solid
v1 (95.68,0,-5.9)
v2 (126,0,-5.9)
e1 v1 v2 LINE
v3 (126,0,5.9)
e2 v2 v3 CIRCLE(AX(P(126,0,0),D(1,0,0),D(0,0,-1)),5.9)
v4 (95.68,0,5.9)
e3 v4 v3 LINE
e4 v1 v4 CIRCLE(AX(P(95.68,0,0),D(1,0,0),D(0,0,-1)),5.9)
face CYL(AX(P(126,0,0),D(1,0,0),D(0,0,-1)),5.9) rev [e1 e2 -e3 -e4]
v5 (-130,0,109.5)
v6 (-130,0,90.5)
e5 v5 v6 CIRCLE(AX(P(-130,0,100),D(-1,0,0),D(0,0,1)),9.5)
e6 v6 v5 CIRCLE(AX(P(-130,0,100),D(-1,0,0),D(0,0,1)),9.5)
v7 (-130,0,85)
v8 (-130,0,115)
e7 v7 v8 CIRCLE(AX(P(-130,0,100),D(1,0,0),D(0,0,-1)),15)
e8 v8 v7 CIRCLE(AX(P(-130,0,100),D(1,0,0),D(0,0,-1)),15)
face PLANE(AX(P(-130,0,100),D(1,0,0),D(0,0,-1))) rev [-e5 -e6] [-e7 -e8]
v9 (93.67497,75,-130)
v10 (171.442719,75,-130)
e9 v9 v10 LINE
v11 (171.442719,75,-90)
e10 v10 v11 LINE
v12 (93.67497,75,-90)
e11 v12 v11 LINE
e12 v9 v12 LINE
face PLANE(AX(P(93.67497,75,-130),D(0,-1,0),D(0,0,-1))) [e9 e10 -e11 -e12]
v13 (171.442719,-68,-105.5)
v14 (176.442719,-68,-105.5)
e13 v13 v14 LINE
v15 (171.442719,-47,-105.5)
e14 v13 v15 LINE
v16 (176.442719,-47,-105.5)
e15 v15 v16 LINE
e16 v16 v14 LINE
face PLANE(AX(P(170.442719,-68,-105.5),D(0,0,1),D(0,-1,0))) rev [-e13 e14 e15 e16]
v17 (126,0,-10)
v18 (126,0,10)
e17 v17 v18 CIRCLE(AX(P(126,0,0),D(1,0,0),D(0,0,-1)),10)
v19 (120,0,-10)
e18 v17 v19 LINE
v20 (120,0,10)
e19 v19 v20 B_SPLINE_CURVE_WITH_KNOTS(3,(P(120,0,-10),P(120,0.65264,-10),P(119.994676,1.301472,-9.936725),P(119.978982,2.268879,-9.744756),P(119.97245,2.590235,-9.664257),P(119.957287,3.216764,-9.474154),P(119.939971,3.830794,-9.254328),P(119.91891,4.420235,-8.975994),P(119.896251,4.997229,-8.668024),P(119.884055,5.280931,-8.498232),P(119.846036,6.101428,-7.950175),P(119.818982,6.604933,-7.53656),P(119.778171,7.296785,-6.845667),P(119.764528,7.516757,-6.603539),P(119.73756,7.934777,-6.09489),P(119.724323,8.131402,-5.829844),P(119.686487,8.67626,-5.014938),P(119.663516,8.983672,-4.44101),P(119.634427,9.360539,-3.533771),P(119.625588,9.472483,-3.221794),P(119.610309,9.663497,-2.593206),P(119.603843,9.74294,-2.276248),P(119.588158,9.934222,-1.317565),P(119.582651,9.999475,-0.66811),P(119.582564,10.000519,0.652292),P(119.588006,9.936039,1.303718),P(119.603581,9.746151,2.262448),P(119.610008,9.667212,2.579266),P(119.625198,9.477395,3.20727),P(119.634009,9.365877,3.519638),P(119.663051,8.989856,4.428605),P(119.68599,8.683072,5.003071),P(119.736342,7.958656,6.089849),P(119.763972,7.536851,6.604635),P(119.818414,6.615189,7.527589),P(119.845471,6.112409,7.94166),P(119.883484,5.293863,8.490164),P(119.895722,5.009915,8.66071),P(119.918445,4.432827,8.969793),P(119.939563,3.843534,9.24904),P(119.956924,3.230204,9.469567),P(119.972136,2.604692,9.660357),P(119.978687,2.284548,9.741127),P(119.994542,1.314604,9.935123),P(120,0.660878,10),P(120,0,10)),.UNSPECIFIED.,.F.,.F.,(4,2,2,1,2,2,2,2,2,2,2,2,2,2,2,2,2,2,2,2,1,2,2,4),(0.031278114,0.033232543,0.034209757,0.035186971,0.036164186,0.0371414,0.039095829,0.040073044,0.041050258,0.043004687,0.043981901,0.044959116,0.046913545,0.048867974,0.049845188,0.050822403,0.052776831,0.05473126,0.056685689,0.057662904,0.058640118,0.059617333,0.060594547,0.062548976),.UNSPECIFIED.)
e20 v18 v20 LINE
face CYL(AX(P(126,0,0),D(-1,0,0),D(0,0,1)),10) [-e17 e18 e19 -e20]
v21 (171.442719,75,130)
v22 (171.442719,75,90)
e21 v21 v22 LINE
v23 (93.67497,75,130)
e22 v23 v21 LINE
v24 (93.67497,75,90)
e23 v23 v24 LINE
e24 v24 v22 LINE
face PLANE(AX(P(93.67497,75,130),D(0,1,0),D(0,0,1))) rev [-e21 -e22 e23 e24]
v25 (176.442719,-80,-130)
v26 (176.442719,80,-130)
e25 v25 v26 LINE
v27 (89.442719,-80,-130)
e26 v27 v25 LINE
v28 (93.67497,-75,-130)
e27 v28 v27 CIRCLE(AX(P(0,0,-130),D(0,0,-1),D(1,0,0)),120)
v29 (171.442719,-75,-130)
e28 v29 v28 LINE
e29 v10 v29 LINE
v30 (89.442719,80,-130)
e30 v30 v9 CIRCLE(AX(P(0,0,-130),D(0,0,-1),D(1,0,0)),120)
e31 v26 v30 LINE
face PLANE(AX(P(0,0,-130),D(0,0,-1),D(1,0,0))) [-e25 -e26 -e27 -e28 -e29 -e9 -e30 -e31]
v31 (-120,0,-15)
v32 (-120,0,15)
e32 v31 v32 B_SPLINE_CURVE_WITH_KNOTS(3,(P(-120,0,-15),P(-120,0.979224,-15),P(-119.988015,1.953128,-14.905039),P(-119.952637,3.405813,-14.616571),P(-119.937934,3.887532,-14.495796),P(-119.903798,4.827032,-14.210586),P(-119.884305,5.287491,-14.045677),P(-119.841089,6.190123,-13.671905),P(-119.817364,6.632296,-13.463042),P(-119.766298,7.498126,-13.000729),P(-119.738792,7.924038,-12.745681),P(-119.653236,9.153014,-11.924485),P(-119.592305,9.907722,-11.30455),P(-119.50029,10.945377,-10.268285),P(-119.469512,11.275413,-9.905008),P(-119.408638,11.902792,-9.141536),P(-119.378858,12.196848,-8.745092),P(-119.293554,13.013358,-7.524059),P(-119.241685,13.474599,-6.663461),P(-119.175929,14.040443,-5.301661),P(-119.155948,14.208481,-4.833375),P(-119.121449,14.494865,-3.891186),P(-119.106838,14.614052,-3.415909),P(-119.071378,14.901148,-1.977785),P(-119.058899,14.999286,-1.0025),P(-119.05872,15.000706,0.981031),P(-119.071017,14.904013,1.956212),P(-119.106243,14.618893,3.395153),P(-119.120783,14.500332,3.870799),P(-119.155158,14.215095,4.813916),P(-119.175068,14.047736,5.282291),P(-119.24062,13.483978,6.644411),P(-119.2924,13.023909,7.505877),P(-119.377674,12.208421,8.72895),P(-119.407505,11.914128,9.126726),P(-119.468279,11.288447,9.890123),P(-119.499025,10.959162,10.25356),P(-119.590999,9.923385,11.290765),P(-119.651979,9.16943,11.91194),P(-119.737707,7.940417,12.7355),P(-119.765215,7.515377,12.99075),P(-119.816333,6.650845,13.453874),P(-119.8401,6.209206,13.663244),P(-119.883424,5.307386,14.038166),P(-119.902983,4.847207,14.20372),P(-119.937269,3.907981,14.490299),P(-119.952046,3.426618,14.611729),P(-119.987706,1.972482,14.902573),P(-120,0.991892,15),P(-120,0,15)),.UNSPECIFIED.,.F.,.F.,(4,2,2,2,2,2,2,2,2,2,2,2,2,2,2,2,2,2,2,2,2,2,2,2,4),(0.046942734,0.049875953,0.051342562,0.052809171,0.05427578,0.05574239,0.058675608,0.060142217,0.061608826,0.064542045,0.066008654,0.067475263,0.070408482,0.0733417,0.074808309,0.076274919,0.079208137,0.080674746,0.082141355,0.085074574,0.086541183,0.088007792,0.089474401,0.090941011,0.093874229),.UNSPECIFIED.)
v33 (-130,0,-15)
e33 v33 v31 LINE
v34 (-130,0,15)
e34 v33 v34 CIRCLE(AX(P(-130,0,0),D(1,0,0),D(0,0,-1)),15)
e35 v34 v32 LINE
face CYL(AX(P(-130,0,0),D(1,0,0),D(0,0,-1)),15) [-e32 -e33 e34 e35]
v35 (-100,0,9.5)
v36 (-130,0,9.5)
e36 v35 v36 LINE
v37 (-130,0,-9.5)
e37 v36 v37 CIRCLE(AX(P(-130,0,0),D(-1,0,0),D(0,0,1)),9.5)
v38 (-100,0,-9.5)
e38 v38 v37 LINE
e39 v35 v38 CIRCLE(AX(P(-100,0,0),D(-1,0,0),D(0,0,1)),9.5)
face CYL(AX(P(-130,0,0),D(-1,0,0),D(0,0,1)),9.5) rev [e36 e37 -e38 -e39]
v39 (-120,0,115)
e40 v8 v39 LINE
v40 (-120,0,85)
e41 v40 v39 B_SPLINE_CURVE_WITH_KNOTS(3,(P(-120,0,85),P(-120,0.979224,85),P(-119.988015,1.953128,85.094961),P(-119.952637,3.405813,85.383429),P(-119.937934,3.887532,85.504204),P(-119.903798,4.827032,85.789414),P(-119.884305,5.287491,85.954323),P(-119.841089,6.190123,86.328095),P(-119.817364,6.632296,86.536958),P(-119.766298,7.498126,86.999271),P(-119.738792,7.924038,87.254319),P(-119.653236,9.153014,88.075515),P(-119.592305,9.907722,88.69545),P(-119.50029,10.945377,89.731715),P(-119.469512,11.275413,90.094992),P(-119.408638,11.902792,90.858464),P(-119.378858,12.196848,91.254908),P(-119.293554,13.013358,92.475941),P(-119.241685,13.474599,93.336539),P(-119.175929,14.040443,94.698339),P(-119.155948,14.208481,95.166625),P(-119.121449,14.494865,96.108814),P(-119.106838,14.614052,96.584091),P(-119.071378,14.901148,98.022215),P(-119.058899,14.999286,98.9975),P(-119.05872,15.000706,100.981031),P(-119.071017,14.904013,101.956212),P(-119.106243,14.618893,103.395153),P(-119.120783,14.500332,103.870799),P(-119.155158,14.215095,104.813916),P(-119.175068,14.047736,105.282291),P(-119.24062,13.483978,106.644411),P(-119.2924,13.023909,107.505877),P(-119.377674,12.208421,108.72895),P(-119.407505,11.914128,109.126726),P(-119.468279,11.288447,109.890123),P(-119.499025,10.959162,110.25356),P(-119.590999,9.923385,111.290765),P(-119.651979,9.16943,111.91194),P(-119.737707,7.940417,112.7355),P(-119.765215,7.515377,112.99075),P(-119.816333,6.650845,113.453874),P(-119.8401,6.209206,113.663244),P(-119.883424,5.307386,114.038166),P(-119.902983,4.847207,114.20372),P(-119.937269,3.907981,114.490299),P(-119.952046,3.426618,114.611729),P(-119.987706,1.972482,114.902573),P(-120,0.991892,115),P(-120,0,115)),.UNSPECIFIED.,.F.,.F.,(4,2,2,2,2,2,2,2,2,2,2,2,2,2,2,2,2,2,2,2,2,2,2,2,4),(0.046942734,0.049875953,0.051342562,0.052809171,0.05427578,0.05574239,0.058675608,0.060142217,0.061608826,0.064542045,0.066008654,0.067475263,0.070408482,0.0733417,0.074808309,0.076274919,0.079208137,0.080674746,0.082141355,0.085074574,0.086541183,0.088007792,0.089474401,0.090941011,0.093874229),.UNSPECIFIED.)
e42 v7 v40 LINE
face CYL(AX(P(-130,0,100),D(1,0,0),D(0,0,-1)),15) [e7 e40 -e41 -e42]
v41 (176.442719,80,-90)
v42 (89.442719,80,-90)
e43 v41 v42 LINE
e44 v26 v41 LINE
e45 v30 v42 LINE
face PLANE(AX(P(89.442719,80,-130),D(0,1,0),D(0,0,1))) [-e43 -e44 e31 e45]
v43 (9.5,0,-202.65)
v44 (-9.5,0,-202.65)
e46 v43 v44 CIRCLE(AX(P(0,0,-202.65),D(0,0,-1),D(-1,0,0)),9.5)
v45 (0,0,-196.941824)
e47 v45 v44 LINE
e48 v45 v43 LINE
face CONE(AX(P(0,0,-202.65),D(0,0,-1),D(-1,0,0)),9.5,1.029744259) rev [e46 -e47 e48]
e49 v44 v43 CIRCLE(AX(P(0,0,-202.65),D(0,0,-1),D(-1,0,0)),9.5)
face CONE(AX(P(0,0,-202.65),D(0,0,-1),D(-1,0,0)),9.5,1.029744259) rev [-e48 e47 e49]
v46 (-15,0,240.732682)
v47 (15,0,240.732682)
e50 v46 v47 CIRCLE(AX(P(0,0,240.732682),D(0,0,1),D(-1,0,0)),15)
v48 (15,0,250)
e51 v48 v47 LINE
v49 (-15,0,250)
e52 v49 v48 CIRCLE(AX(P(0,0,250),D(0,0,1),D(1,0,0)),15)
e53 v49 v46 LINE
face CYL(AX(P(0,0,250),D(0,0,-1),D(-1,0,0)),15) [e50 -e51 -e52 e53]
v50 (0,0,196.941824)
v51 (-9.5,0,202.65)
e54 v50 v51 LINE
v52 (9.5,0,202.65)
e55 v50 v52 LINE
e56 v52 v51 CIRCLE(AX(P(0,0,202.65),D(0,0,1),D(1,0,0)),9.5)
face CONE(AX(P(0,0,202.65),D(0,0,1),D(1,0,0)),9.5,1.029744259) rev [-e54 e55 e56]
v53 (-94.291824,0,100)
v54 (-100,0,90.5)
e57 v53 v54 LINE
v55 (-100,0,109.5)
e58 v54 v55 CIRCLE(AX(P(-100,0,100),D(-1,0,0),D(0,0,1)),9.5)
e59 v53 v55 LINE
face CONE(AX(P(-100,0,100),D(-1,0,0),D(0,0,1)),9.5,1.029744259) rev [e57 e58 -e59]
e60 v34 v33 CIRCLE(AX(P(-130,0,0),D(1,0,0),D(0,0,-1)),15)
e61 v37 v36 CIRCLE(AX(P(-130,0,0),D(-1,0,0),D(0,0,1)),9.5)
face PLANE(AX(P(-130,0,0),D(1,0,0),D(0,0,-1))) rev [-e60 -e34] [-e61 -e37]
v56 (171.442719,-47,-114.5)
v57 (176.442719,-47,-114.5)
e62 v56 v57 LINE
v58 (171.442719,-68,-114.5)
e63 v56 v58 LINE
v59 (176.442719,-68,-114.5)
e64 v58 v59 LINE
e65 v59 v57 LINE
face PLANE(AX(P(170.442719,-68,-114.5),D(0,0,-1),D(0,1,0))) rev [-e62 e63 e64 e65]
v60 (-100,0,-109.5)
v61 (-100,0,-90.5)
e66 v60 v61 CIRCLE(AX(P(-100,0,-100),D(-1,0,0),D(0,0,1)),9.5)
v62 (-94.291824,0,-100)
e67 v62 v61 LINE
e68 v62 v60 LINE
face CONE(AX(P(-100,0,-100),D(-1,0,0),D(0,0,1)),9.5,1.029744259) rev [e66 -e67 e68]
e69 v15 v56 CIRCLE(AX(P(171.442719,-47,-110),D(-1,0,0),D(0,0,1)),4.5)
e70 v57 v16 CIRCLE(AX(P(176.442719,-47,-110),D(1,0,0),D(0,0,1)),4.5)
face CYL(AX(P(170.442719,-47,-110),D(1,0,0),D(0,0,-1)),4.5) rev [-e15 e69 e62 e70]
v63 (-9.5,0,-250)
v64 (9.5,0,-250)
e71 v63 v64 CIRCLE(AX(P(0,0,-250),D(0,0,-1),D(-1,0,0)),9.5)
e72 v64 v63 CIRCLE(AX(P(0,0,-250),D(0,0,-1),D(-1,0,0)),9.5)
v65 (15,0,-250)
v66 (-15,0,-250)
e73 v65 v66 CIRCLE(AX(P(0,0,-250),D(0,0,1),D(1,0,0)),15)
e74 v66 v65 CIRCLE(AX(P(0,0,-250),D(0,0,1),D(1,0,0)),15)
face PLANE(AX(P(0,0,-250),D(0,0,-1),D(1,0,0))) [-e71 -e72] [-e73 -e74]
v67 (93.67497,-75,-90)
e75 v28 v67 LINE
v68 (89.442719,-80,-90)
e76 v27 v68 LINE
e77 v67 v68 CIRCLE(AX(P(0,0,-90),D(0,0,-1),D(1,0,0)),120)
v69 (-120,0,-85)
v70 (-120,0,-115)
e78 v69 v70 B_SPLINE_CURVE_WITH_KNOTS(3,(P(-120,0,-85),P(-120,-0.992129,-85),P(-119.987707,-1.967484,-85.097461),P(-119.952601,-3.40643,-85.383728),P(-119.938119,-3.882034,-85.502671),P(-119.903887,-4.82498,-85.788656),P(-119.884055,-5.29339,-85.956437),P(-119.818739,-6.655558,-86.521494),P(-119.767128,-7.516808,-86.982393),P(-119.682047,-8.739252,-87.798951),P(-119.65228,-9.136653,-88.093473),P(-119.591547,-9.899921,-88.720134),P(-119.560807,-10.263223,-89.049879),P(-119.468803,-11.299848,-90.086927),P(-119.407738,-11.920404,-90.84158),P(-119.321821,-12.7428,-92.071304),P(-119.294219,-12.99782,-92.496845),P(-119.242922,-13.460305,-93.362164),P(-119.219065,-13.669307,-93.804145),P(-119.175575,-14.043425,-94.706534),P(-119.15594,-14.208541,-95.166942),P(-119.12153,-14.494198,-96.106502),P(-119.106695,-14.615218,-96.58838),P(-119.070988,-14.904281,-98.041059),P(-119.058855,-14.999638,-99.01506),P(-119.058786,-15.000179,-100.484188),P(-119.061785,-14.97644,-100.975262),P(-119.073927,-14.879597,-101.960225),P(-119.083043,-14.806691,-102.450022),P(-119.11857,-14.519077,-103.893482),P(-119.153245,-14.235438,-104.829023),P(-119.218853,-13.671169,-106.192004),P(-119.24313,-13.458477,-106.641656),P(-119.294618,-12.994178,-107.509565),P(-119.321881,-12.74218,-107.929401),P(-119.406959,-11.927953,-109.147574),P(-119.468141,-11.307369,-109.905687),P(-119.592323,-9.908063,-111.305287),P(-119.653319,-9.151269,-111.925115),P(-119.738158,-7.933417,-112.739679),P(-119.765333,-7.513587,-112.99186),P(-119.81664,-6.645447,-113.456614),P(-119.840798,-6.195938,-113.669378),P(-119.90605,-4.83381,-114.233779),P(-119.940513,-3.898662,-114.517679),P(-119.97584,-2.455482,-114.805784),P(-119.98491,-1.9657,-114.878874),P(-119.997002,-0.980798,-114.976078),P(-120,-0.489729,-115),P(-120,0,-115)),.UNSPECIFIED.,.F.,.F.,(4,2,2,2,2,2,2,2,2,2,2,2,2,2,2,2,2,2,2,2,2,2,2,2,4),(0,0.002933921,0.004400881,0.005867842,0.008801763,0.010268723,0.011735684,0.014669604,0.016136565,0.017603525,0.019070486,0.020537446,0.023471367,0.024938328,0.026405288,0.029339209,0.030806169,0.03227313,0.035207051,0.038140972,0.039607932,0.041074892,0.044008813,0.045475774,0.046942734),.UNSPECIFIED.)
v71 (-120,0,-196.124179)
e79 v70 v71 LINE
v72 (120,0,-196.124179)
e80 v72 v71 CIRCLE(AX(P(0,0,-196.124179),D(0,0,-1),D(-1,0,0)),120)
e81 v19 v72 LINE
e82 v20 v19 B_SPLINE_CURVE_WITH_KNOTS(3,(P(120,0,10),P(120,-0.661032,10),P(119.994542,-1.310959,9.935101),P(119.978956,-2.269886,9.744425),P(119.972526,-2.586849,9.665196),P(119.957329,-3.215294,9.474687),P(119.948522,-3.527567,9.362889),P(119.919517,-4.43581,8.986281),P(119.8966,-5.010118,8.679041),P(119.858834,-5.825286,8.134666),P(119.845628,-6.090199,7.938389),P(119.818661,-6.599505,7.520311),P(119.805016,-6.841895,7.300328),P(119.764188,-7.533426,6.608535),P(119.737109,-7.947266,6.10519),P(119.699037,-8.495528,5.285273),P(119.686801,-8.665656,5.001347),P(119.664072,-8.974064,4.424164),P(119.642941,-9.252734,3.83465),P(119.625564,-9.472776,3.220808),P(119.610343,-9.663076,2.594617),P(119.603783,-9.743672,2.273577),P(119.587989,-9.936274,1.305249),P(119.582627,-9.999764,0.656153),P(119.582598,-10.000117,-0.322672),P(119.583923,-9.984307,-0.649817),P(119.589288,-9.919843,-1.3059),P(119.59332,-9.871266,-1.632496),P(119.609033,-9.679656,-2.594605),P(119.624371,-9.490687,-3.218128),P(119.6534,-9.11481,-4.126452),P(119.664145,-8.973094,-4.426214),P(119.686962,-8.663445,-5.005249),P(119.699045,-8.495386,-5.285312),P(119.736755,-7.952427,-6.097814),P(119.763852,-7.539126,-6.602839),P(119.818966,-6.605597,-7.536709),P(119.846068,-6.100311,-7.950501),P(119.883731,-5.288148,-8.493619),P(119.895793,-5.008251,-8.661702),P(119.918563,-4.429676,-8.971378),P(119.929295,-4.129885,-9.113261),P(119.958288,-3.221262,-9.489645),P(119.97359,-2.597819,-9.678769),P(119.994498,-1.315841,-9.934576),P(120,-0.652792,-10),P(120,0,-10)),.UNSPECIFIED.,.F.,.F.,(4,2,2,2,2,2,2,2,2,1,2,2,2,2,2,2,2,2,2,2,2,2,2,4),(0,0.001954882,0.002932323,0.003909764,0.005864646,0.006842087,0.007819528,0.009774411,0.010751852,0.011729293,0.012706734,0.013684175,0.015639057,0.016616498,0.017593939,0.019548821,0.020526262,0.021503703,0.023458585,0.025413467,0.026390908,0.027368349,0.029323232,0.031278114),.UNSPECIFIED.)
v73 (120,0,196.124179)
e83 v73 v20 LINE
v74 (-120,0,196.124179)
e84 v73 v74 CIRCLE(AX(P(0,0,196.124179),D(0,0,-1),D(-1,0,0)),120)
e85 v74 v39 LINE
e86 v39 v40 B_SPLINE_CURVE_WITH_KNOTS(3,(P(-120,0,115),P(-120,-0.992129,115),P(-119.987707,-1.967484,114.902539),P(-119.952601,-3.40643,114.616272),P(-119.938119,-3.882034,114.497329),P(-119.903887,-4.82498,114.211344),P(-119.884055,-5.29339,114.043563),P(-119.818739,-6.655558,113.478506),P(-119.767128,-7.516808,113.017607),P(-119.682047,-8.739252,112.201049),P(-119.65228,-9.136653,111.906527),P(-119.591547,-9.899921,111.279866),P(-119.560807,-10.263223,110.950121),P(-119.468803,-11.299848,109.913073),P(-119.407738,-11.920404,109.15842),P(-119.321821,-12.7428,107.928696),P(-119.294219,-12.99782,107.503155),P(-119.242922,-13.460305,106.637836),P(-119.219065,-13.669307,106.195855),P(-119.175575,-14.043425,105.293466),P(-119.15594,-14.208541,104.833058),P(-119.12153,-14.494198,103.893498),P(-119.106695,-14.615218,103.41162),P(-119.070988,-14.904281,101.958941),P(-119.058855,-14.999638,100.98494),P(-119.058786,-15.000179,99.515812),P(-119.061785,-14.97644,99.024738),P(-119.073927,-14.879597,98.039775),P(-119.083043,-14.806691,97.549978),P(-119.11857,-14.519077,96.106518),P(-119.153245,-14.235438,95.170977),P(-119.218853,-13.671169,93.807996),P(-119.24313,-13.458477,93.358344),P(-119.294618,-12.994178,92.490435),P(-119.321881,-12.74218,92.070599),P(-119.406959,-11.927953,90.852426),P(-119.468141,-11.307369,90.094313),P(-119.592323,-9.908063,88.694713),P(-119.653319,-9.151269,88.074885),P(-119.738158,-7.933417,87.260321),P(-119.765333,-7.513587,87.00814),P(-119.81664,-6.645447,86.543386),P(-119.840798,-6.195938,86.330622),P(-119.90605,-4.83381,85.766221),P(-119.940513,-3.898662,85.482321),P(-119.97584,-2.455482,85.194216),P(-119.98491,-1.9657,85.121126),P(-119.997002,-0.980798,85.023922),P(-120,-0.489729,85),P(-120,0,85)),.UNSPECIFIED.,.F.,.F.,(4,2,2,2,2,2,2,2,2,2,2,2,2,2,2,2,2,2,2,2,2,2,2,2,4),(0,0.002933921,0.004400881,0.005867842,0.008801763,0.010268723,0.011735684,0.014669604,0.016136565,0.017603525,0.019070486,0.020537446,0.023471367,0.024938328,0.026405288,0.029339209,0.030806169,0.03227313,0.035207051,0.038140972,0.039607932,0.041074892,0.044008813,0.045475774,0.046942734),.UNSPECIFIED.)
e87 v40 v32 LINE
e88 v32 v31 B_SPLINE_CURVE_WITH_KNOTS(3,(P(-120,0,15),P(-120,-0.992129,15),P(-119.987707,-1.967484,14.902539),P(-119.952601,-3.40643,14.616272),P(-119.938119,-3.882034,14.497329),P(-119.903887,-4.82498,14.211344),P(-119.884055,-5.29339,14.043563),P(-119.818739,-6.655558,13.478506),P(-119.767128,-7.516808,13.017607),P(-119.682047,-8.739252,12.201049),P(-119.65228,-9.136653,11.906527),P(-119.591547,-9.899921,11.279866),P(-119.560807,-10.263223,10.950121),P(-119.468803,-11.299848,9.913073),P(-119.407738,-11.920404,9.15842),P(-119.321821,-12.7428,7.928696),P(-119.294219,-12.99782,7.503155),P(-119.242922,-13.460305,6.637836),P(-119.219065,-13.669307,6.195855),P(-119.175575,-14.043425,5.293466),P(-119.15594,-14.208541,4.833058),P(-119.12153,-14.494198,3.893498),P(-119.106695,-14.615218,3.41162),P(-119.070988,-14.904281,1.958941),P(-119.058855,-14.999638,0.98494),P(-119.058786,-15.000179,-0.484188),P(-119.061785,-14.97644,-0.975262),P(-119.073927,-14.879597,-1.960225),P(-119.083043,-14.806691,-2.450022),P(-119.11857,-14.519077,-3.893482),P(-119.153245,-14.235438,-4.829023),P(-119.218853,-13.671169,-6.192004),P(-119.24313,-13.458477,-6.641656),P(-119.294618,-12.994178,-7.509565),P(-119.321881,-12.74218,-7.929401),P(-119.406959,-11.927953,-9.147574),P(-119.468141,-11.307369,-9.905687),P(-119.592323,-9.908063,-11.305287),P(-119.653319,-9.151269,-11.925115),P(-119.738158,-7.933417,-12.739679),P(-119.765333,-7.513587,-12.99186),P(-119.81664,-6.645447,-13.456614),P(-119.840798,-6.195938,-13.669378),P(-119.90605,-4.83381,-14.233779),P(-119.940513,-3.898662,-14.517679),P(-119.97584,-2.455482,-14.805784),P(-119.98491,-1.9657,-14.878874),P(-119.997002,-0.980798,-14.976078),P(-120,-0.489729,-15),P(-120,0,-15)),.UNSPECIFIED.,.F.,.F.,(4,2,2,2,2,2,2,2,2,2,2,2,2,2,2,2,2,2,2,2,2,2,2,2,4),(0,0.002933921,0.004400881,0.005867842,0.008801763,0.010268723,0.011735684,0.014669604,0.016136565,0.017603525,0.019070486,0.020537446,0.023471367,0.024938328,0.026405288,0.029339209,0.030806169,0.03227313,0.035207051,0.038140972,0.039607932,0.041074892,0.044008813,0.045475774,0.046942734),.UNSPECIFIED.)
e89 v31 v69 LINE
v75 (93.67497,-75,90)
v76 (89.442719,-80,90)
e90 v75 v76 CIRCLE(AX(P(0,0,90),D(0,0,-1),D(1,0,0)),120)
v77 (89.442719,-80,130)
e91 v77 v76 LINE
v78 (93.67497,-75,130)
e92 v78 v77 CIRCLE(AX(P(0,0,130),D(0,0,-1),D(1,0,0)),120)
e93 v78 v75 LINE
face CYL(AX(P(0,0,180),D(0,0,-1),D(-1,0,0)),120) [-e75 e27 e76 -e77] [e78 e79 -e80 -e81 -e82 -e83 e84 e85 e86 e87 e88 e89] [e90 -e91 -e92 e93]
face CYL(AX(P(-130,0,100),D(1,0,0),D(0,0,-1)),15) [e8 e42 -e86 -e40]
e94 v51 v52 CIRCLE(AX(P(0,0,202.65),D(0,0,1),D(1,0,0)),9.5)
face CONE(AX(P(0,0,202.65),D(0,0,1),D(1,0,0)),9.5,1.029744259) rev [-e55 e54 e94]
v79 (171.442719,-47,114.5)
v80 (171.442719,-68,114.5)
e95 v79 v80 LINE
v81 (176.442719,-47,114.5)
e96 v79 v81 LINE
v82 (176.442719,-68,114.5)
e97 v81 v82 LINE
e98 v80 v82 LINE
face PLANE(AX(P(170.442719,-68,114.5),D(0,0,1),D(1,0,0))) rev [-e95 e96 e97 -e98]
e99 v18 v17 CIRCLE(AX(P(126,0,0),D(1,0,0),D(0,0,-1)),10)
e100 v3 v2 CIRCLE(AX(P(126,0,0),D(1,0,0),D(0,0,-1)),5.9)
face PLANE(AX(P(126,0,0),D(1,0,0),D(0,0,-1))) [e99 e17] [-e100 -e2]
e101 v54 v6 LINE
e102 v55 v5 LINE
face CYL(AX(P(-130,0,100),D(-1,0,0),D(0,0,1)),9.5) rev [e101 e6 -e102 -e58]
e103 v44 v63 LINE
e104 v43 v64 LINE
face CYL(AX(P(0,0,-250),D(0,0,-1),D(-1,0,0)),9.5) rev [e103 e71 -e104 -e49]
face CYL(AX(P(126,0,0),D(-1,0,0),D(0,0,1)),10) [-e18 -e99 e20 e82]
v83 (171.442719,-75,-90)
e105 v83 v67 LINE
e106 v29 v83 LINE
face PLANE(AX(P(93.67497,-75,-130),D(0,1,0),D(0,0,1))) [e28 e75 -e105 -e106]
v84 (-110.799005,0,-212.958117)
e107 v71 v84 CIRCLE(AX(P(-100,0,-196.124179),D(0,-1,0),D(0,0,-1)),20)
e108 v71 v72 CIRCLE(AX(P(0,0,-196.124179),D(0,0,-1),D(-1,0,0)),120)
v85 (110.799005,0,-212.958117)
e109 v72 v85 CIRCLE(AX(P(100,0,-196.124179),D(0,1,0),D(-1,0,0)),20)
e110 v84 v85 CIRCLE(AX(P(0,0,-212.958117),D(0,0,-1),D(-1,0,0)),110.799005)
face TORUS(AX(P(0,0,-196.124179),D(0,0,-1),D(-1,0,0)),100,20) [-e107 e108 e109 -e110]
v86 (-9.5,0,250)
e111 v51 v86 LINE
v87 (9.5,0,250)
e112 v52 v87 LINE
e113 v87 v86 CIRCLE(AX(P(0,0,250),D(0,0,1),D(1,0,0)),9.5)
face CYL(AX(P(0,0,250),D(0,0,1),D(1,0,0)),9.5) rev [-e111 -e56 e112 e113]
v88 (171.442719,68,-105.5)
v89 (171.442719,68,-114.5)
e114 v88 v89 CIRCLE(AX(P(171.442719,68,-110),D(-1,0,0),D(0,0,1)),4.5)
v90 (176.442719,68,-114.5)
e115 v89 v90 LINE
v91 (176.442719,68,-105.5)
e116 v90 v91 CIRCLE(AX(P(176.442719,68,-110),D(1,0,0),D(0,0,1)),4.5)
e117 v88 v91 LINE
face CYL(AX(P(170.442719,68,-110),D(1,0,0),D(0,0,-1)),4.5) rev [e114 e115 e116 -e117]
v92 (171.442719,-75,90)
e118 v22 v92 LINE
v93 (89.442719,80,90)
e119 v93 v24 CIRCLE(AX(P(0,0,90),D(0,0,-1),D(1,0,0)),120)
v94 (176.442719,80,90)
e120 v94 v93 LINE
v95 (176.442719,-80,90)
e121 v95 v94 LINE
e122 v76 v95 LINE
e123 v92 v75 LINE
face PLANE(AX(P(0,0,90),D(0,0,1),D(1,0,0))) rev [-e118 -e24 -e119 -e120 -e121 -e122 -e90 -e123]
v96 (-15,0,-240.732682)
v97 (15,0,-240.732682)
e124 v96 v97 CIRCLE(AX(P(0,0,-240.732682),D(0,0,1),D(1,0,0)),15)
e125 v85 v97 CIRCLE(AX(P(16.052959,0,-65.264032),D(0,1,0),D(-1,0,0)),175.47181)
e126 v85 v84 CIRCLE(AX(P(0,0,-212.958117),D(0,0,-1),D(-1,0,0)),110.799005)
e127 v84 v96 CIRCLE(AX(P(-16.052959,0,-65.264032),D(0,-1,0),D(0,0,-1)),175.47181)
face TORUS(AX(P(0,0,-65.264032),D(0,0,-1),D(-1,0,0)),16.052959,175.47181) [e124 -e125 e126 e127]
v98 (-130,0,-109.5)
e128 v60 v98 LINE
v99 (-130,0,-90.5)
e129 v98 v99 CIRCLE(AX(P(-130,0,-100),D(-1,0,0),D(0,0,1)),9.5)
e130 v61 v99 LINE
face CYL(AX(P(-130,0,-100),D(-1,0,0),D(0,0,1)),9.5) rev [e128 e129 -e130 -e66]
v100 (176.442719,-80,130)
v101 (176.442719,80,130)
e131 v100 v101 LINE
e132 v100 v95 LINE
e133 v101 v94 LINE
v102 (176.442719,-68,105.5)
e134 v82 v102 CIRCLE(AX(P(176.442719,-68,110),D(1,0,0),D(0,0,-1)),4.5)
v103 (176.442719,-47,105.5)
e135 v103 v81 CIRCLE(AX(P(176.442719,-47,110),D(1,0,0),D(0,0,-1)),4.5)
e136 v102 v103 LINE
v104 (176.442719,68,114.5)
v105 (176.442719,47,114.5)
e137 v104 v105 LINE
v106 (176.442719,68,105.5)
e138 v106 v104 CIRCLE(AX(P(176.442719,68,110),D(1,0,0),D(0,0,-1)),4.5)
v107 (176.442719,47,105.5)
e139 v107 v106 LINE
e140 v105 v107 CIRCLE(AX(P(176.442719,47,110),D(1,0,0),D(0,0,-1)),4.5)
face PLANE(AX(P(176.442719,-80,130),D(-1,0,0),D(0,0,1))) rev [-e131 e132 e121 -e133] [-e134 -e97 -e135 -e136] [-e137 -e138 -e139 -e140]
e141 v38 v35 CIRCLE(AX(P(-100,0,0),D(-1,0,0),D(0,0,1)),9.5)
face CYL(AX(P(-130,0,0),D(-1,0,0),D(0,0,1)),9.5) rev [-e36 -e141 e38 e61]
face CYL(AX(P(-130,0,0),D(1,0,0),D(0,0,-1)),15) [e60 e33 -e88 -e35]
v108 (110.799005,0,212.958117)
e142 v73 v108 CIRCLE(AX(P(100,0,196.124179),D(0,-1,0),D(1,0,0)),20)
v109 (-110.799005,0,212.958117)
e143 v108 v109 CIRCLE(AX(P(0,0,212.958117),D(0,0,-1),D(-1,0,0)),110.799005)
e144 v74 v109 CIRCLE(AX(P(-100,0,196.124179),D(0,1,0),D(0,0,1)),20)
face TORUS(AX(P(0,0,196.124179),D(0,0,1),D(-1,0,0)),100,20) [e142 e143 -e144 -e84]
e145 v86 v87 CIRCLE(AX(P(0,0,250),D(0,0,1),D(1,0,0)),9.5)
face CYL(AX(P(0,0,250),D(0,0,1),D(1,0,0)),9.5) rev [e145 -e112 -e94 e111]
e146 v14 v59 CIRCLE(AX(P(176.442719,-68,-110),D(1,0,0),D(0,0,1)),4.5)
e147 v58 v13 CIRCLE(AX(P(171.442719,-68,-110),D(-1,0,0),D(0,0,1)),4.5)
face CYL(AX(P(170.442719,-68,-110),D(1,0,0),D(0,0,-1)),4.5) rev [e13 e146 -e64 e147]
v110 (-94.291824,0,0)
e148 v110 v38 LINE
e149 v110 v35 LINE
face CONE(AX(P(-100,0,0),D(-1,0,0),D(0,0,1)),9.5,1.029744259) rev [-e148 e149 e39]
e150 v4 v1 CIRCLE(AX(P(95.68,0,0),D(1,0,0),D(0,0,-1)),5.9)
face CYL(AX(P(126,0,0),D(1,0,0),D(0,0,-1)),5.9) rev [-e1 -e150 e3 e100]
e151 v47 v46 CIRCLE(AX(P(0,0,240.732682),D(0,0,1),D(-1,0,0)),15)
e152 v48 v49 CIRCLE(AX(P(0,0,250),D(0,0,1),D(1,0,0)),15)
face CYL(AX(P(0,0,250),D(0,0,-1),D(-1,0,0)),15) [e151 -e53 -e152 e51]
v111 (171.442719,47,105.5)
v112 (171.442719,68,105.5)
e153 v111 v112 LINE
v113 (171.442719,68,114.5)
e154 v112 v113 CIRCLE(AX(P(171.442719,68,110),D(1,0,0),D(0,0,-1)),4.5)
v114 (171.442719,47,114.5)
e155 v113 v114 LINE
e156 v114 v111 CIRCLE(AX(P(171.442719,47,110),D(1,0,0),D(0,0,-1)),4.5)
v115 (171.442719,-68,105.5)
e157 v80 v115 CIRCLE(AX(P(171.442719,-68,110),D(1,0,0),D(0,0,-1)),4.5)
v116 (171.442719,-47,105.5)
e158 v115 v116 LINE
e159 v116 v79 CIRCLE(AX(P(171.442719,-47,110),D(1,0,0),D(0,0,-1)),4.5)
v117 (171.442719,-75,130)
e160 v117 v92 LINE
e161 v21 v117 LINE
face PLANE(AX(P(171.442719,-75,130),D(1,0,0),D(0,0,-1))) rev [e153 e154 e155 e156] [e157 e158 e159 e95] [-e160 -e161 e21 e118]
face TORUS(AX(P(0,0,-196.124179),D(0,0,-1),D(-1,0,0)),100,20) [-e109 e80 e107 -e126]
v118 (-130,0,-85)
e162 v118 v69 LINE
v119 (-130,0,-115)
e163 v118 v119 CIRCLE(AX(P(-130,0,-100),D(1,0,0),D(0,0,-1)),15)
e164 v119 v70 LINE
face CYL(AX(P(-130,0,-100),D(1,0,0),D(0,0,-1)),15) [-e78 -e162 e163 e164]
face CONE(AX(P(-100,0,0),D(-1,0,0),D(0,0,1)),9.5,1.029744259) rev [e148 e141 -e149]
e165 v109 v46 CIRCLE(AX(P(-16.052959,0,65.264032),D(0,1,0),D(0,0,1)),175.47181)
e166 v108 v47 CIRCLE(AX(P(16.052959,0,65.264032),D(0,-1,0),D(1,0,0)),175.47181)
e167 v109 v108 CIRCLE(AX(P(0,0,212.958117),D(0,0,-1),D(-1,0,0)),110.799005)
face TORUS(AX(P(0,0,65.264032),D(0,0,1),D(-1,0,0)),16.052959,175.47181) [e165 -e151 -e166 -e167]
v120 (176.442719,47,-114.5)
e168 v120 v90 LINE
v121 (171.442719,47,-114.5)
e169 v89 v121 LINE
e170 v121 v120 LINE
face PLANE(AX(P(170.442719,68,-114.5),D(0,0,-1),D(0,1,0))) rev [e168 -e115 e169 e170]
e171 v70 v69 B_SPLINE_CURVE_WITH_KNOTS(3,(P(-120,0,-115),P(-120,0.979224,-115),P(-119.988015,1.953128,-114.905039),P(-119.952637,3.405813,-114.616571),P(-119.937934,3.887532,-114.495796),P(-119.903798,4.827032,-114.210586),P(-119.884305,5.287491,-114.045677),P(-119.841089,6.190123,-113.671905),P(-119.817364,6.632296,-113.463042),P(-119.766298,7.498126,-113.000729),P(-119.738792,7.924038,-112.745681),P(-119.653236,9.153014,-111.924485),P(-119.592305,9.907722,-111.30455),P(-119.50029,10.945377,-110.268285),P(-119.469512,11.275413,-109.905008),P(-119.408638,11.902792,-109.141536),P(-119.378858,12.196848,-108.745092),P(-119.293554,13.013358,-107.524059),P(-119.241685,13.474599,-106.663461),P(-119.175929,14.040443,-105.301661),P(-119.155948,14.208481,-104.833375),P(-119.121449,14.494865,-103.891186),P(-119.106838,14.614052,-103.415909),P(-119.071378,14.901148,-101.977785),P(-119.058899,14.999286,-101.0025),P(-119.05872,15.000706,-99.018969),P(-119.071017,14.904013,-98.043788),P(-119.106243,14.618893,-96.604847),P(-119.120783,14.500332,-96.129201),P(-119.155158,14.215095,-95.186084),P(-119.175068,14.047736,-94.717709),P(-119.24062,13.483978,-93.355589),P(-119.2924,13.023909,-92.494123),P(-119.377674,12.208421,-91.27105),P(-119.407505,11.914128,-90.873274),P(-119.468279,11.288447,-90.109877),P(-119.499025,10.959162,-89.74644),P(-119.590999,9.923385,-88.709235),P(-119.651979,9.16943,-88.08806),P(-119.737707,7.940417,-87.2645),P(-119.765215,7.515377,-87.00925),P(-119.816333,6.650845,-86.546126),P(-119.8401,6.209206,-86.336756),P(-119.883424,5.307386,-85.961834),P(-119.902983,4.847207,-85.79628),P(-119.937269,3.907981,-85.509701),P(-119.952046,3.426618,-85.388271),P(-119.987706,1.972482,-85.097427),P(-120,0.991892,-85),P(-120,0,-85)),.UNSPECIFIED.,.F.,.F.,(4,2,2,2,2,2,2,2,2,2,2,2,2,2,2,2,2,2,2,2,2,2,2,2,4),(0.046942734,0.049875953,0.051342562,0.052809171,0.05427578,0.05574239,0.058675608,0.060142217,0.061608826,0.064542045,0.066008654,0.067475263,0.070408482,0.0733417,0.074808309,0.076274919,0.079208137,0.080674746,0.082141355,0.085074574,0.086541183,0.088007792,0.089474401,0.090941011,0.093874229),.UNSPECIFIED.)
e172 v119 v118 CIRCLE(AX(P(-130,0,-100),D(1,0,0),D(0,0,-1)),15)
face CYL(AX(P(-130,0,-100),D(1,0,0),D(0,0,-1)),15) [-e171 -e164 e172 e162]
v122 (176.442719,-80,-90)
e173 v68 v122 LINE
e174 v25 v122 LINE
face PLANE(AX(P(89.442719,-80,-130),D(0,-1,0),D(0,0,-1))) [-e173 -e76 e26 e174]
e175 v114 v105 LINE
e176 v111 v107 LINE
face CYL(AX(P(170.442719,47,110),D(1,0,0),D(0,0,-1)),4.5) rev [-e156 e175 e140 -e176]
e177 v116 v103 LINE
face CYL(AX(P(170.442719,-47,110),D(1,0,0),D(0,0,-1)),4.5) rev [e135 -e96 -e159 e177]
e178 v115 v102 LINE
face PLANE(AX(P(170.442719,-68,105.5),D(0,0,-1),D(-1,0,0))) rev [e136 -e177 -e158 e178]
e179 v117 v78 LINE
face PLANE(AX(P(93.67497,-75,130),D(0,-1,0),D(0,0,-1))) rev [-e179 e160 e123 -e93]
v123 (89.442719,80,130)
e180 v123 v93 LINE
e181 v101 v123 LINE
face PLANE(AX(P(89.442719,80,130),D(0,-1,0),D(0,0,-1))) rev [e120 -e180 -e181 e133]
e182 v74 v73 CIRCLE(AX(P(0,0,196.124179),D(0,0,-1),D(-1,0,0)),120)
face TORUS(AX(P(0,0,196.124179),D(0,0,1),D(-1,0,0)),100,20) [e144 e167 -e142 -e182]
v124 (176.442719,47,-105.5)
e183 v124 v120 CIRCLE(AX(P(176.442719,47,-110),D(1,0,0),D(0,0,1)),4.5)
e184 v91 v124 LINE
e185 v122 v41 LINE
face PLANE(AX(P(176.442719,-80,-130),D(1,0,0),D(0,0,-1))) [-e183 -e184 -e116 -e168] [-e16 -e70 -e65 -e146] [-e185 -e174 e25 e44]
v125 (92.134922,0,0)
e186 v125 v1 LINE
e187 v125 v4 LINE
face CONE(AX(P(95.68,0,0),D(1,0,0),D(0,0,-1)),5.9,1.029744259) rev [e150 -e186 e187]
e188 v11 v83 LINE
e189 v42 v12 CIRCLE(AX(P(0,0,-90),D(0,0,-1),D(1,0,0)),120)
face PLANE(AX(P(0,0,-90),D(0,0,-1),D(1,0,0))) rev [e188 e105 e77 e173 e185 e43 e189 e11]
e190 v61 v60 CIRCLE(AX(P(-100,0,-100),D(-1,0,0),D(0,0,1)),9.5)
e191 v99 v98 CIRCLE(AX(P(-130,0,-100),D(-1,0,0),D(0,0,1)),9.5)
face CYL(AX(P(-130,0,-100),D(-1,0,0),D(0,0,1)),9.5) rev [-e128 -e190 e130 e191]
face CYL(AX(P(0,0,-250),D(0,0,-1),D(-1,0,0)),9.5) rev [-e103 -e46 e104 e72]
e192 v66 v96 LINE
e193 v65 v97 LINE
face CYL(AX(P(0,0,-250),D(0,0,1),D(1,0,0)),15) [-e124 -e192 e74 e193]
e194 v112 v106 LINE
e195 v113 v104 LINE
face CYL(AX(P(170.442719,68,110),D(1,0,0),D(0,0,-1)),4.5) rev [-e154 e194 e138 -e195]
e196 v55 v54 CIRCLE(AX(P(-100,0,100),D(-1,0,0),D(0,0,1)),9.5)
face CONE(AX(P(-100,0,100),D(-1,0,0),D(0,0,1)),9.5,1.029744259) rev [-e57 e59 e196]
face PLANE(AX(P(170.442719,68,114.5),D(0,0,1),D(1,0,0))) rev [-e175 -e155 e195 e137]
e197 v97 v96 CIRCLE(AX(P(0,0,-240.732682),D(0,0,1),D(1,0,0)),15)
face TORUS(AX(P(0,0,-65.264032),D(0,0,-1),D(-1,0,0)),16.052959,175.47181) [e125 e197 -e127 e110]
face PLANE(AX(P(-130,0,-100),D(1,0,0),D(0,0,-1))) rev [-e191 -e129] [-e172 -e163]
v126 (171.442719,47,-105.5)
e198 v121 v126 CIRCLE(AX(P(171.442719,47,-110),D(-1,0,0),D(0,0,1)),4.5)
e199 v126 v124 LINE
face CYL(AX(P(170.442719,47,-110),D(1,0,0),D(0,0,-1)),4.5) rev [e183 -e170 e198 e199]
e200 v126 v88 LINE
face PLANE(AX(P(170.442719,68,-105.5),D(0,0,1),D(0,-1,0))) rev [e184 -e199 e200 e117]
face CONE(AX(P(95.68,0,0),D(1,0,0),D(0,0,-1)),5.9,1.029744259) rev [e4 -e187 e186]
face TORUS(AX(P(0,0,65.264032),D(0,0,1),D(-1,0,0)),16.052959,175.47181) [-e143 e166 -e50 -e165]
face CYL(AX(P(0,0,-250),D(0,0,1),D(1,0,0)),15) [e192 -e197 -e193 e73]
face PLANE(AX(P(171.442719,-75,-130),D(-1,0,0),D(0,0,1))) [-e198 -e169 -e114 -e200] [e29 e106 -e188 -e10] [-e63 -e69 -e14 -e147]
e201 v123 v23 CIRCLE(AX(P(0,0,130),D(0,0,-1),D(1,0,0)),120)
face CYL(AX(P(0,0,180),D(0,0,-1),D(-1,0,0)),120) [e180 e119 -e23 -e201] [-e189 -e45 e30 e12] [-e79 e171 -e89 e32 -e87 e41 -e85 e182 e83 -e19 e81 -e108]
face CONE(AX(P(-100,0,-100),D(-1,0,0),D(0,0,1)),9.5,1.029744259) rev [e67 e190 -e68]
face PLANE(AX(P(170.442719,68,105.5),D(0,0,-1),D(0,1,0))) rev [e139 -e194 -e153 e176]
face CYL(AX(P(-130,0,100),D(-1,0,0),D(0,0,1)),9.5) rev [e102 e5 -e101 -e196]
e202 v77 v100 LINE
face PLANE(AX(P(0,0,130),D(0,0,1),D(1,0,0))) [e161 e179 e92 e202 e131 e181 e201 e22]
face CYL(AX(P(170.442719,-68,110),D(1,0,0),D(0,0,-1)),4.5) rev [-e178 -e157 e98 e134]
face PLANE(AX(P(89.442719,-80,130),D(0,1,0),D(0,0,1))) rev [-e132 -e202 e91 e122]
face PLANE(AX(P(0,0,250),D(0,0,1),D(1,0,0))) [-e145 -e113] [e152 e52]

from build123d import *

# Parameters (mm, degrees)
SKETCH_1_R               = 120
EXTRUDE_1_DEPTH          = 180
EXTRUDE_2_DEPTH          = 20
CUT_EXTRUDE_1_DEPTH      = 6
SKETCH_17_R              = 15
EXTRUDE_3_DEPTH          = 20
HOLE_WIZARD_G1_2_1_D     = 19
HOLE_WIZARD_G1_2_1_DEPTH = 30
HOLE_WIZARD_G1_2_1_TIP   = 5.708175881
SKETCH_20_R              = 15
EXTRUDE_4_DEPTH          = 15
HOLE_WIZARD_G1_2_2_D     = 19
HOLE_WIZARD_G1_2_2_DEPTH = 47.35
HOLE_WIZARD_G1_2_2_TIP   = 5.708175881
HOLE_WIZARD_G1_2_3_D     = 19
HOLE_WIZARD_G1_2_3_DEPTH = 47.35
HOLE_WIZARD_G1_2_3_TIP   = 5.708175881
SKETCH_26_R              = 10
EXTRUDE_5_DEPTH          = 16
HOLE_WIZARD_G1_4_1_D     = 11.8
HOLE_WIZARD_G1_4_1_DEPTH = 30.32
HOLE_WIZARD_G1_4_1_TIP   = 3.545077652


with BuildPart() as part:
    # 草图1 → 凸台-拉伸1 (new, symmetric)
    with BuildSketch(Plane.XY):
        with Locations(Location((0, 0, 0), (0, 0, 180))):
            Circle(SKETCH_1_R)
    extrude(amount=EXTRUDE_1_DEPTH, both=True)

    # 草图2 → 旋转1 (revolve)
    with BuildSketch(Plane(origin=(0, 0, 0), x_dir=(1, 0, 0), z_dir=(0, 1, 0)), mode=Mode.PRIVATE) as revolve_1_sk:
        with BuildLine():
            Line((0, 180), (120, 180))
            Line((120, 180), (120, 196.124178579))
            ThreePointArc((120, 196.124178579), (117.549645232, 205.716360408), (110.799004776, 212.958117388))
            ThreePointArc((110.799004776, 212.958117388), (57.657842502, 235.732180627), (0, 240))
            Line((0, 240), (0, 180))
        make_face()
    revolve_1 = revolve(revolve_1_sk.sketch.rotate(Axis((0, 0, -180), (0, 0, 1)), 180), axis=Axis((0, 0, -180), (0, 0, 1)))

    # 镜向1: 旋转1 across plane
    add(revolve_1.mirror(Plane.XY))

    # 草图15 → 凸台-拉伸2 (add, symmetric)
    with BuildSketch(Plane.XY.offset(110)):
        with BuildLine():
            Line((93.674969976, -75), (171.4427191, -75))
            Line((171.4427191, -75), (171.4427191, 75))
            Line((171.4427191, 75), (93.674969976, 75))
            ThreePointArc((93.674969976, 75), (91.592969234, 77.528884855), (89.4427191, 80))
            Line((89.4427191, 80), (176.4427191, 80))
            Line((176.4427191, 80), (176.4427191, -80))
            Line((176.4427191, -80), (89.4427191, -80))
            ThreePointArc((89.4427191, -80), (91.592969234, -77.528884855), (93.674969976, -75))
        make_face()
    extrude_2 = extrude(amount=EXTRUDE_2_DEPTH, both=True)

    # 镜向2: 凸台-拉伸2 across plane
    add(extrude_2.mirror(Plane.XY))

    # 草图16 → 切除-拉伸1 (cut)
    with BuildSketch(Plane(origin=(176.4427191, 0, 0), x_dir=(0, 0, -1), z_dir=(1, 0, 0))):
        with BuildLine():
            Line((-105.5, 68), (-105.5, 47))
            ThreePointArc((-105.5, 47), (-110, 42.5), (-114.5, 47))
            Line((-114.5, 47), (-114.5, 68))
            ThreePointArc((-114.5, 68), (-110, 72.5), (-105.5, 68))
        make_face()
        with BuildLine():
            Line((-114.5, -68), (-114.5, -47))
            ThreePointArc((-114.5, -47), (-110, -42.5), (-105.5, -47))
            Line((-105.5, -47), (-105.5, -68))
            ThreePointArc((-105.5, -68), (-110, -72.5), (-114.5, -68))
        make_face()
        with BuildLine():
            Line((105.5, 68), (105.5, 47))
            ThreePointArc((105.5, 47), (110, 42.5), (114.5, 47))
            Line((114.5, 47), (114.5, 68))
            ThreePointArc((114.5, 68), (110, 72.5), (105.5, 68))
        make_face()
        with BuildLine():
            Line((114.5, -68), (114.5, -47))
            ThreePointArc((114.5, -47), (110, -42.5), (105.5, -47))
            Line((105.5, -47), (105.5, -68))
            ThreePointArc((105.5, -68), (110, -72.5), (114.5, -68))
        make_face()
    extrude(amount=-CUT_EXTRUDE_1_DEPTH, mode=Mode.SUBTRACT)

    # 草图17 → 凸台-拉伸3 (add)
    with BuildSketch(Plane(origin=(-110, 0, 0), x_dir=(0, 0, -1), z_dir=(1, 0, 0))):
        Circle(SKETCH_17_R)
        with Locations((100, 0)):
            Circle(SKETCH_17_R)
        with Locations((-100, 0)):
            Circle(SKETCH_17_R)
    extrude(amount=-EXTRUDE_3_DEPTH)

    # G1/2 螺纹孔1
    with Locations(Plane.ZY.offset(130)):
        with Locations((-100, 0), (0, 0), (100, 0)):
            Hole(HOLE_WIZARD_G1_2_1_D / 2, depth=HOLE_WIZARD_G1_2_1_DEPTH)
            with Locations((0, 0, -(HOLE_WIZARD_G1_2_1_DEPTH + HOLE_WIZARD_G1_2_1_TIP / 2))):  # 118° drill point
                Cone(0, HOLE_WIZARD_G1_2_1_D / 2, HOLE_WIZARD_G1_2_1_TIP, mode=Mode.SUBTRACT)

    # 草图20 → 凸台-拉伸4 (add)
    with BuildSketch(Plane.XY.offset(235)):
        with Locations(Location((0, 0, 0), (0, 0, 180))):
            Circle(SKETCH_20_R)
    extrude_4 = extrude(amount=EXTRUDE_4_DEPTH)

    # G1/2 螺纹孔2
    with Locations(Plane.XY.offset(250)):
        with Locations((0, 0)):
            Hole(HOLE_WIZARD_G1_2_2_D / 2, depth=HOLE_WIZARD_G1_2_2_DEPTH)
            with Locations((0, 0, -(HOLE_WIZARD_G1_2_2_DEPTH + HOLE_WIZARD_G1_2_2_TIP / 2))):  # 118° drill point
                Cone(0, HOLE_WIZARD_G1_2_2_D / 2, HOLE_WIZARD_G1_2_2_TIP, mode=Mode.SUBTRACT)

    # 镜向3: 凸台-拉伸4 across plane
    add(extrude_4.mirror(Plane.XY))

    # G1/2 螺纹孔3
    with Locations(Plane(origin=(0, 0, -250), x_dir=(-1, 0, 0), z_dir=(0, 0, -1))):
        with Locations((0, 0)):
            Hole(HOLE_WIZARD_G1_2_3_D / 2, depth=HOLE_WIZARD_G1_2_3_DEPTH)
            with Locations((0, 0, -(HOLE_WIZARD_G1_2_3_DEPTH + HOLE_WIZARD_G1_2_3_TIP / 2))):  # 118° drill point
                Cone(0, HOLE_WIZARD_G1_2_3_D / 2, HOLE_WIZARD_G1_2_3_TIP, mode=Mode.SUBTRACT)

    # 草图26 → 凸台-拉伸5 (add)
    with BuildSketch(Plane(origin=(110, 0, 0), x_dir=(0, 0, -1), z_dir=(1, 0, 0))):
        with Locations(Location((0, 0, 0), (0, 0, 180))):
            Circle(SKETCH_26_R)
    extrude(amount=EXTRUDE_5_DEPTH)

    # G1/4 螺纹孔1
    with Locations(Plane(origin=(126, 0, 0), x_dir=(0, 0, -1), z_dir=(1, 0, 0))):
        with Locations((0, 0)):
            Hole(HOLE_WIZARD_G1_4_1_D / 2, depth=HOLE_WIZARD_G1_4_1_DEPTH)
            with Locations((0, 0, -(HOLE_WIZARD_G1_4_1_DEPTH + HOLE_WIZARD_G1_4_1_TIP / 2))):  # 118° drill point
                Cone(0, HOLE_WIZARD_G1_4_1_D / 2, HOLE_WIZARD_G1_4_1_TIP, mode=Mode.SUBTRACT)


solid = part.part
